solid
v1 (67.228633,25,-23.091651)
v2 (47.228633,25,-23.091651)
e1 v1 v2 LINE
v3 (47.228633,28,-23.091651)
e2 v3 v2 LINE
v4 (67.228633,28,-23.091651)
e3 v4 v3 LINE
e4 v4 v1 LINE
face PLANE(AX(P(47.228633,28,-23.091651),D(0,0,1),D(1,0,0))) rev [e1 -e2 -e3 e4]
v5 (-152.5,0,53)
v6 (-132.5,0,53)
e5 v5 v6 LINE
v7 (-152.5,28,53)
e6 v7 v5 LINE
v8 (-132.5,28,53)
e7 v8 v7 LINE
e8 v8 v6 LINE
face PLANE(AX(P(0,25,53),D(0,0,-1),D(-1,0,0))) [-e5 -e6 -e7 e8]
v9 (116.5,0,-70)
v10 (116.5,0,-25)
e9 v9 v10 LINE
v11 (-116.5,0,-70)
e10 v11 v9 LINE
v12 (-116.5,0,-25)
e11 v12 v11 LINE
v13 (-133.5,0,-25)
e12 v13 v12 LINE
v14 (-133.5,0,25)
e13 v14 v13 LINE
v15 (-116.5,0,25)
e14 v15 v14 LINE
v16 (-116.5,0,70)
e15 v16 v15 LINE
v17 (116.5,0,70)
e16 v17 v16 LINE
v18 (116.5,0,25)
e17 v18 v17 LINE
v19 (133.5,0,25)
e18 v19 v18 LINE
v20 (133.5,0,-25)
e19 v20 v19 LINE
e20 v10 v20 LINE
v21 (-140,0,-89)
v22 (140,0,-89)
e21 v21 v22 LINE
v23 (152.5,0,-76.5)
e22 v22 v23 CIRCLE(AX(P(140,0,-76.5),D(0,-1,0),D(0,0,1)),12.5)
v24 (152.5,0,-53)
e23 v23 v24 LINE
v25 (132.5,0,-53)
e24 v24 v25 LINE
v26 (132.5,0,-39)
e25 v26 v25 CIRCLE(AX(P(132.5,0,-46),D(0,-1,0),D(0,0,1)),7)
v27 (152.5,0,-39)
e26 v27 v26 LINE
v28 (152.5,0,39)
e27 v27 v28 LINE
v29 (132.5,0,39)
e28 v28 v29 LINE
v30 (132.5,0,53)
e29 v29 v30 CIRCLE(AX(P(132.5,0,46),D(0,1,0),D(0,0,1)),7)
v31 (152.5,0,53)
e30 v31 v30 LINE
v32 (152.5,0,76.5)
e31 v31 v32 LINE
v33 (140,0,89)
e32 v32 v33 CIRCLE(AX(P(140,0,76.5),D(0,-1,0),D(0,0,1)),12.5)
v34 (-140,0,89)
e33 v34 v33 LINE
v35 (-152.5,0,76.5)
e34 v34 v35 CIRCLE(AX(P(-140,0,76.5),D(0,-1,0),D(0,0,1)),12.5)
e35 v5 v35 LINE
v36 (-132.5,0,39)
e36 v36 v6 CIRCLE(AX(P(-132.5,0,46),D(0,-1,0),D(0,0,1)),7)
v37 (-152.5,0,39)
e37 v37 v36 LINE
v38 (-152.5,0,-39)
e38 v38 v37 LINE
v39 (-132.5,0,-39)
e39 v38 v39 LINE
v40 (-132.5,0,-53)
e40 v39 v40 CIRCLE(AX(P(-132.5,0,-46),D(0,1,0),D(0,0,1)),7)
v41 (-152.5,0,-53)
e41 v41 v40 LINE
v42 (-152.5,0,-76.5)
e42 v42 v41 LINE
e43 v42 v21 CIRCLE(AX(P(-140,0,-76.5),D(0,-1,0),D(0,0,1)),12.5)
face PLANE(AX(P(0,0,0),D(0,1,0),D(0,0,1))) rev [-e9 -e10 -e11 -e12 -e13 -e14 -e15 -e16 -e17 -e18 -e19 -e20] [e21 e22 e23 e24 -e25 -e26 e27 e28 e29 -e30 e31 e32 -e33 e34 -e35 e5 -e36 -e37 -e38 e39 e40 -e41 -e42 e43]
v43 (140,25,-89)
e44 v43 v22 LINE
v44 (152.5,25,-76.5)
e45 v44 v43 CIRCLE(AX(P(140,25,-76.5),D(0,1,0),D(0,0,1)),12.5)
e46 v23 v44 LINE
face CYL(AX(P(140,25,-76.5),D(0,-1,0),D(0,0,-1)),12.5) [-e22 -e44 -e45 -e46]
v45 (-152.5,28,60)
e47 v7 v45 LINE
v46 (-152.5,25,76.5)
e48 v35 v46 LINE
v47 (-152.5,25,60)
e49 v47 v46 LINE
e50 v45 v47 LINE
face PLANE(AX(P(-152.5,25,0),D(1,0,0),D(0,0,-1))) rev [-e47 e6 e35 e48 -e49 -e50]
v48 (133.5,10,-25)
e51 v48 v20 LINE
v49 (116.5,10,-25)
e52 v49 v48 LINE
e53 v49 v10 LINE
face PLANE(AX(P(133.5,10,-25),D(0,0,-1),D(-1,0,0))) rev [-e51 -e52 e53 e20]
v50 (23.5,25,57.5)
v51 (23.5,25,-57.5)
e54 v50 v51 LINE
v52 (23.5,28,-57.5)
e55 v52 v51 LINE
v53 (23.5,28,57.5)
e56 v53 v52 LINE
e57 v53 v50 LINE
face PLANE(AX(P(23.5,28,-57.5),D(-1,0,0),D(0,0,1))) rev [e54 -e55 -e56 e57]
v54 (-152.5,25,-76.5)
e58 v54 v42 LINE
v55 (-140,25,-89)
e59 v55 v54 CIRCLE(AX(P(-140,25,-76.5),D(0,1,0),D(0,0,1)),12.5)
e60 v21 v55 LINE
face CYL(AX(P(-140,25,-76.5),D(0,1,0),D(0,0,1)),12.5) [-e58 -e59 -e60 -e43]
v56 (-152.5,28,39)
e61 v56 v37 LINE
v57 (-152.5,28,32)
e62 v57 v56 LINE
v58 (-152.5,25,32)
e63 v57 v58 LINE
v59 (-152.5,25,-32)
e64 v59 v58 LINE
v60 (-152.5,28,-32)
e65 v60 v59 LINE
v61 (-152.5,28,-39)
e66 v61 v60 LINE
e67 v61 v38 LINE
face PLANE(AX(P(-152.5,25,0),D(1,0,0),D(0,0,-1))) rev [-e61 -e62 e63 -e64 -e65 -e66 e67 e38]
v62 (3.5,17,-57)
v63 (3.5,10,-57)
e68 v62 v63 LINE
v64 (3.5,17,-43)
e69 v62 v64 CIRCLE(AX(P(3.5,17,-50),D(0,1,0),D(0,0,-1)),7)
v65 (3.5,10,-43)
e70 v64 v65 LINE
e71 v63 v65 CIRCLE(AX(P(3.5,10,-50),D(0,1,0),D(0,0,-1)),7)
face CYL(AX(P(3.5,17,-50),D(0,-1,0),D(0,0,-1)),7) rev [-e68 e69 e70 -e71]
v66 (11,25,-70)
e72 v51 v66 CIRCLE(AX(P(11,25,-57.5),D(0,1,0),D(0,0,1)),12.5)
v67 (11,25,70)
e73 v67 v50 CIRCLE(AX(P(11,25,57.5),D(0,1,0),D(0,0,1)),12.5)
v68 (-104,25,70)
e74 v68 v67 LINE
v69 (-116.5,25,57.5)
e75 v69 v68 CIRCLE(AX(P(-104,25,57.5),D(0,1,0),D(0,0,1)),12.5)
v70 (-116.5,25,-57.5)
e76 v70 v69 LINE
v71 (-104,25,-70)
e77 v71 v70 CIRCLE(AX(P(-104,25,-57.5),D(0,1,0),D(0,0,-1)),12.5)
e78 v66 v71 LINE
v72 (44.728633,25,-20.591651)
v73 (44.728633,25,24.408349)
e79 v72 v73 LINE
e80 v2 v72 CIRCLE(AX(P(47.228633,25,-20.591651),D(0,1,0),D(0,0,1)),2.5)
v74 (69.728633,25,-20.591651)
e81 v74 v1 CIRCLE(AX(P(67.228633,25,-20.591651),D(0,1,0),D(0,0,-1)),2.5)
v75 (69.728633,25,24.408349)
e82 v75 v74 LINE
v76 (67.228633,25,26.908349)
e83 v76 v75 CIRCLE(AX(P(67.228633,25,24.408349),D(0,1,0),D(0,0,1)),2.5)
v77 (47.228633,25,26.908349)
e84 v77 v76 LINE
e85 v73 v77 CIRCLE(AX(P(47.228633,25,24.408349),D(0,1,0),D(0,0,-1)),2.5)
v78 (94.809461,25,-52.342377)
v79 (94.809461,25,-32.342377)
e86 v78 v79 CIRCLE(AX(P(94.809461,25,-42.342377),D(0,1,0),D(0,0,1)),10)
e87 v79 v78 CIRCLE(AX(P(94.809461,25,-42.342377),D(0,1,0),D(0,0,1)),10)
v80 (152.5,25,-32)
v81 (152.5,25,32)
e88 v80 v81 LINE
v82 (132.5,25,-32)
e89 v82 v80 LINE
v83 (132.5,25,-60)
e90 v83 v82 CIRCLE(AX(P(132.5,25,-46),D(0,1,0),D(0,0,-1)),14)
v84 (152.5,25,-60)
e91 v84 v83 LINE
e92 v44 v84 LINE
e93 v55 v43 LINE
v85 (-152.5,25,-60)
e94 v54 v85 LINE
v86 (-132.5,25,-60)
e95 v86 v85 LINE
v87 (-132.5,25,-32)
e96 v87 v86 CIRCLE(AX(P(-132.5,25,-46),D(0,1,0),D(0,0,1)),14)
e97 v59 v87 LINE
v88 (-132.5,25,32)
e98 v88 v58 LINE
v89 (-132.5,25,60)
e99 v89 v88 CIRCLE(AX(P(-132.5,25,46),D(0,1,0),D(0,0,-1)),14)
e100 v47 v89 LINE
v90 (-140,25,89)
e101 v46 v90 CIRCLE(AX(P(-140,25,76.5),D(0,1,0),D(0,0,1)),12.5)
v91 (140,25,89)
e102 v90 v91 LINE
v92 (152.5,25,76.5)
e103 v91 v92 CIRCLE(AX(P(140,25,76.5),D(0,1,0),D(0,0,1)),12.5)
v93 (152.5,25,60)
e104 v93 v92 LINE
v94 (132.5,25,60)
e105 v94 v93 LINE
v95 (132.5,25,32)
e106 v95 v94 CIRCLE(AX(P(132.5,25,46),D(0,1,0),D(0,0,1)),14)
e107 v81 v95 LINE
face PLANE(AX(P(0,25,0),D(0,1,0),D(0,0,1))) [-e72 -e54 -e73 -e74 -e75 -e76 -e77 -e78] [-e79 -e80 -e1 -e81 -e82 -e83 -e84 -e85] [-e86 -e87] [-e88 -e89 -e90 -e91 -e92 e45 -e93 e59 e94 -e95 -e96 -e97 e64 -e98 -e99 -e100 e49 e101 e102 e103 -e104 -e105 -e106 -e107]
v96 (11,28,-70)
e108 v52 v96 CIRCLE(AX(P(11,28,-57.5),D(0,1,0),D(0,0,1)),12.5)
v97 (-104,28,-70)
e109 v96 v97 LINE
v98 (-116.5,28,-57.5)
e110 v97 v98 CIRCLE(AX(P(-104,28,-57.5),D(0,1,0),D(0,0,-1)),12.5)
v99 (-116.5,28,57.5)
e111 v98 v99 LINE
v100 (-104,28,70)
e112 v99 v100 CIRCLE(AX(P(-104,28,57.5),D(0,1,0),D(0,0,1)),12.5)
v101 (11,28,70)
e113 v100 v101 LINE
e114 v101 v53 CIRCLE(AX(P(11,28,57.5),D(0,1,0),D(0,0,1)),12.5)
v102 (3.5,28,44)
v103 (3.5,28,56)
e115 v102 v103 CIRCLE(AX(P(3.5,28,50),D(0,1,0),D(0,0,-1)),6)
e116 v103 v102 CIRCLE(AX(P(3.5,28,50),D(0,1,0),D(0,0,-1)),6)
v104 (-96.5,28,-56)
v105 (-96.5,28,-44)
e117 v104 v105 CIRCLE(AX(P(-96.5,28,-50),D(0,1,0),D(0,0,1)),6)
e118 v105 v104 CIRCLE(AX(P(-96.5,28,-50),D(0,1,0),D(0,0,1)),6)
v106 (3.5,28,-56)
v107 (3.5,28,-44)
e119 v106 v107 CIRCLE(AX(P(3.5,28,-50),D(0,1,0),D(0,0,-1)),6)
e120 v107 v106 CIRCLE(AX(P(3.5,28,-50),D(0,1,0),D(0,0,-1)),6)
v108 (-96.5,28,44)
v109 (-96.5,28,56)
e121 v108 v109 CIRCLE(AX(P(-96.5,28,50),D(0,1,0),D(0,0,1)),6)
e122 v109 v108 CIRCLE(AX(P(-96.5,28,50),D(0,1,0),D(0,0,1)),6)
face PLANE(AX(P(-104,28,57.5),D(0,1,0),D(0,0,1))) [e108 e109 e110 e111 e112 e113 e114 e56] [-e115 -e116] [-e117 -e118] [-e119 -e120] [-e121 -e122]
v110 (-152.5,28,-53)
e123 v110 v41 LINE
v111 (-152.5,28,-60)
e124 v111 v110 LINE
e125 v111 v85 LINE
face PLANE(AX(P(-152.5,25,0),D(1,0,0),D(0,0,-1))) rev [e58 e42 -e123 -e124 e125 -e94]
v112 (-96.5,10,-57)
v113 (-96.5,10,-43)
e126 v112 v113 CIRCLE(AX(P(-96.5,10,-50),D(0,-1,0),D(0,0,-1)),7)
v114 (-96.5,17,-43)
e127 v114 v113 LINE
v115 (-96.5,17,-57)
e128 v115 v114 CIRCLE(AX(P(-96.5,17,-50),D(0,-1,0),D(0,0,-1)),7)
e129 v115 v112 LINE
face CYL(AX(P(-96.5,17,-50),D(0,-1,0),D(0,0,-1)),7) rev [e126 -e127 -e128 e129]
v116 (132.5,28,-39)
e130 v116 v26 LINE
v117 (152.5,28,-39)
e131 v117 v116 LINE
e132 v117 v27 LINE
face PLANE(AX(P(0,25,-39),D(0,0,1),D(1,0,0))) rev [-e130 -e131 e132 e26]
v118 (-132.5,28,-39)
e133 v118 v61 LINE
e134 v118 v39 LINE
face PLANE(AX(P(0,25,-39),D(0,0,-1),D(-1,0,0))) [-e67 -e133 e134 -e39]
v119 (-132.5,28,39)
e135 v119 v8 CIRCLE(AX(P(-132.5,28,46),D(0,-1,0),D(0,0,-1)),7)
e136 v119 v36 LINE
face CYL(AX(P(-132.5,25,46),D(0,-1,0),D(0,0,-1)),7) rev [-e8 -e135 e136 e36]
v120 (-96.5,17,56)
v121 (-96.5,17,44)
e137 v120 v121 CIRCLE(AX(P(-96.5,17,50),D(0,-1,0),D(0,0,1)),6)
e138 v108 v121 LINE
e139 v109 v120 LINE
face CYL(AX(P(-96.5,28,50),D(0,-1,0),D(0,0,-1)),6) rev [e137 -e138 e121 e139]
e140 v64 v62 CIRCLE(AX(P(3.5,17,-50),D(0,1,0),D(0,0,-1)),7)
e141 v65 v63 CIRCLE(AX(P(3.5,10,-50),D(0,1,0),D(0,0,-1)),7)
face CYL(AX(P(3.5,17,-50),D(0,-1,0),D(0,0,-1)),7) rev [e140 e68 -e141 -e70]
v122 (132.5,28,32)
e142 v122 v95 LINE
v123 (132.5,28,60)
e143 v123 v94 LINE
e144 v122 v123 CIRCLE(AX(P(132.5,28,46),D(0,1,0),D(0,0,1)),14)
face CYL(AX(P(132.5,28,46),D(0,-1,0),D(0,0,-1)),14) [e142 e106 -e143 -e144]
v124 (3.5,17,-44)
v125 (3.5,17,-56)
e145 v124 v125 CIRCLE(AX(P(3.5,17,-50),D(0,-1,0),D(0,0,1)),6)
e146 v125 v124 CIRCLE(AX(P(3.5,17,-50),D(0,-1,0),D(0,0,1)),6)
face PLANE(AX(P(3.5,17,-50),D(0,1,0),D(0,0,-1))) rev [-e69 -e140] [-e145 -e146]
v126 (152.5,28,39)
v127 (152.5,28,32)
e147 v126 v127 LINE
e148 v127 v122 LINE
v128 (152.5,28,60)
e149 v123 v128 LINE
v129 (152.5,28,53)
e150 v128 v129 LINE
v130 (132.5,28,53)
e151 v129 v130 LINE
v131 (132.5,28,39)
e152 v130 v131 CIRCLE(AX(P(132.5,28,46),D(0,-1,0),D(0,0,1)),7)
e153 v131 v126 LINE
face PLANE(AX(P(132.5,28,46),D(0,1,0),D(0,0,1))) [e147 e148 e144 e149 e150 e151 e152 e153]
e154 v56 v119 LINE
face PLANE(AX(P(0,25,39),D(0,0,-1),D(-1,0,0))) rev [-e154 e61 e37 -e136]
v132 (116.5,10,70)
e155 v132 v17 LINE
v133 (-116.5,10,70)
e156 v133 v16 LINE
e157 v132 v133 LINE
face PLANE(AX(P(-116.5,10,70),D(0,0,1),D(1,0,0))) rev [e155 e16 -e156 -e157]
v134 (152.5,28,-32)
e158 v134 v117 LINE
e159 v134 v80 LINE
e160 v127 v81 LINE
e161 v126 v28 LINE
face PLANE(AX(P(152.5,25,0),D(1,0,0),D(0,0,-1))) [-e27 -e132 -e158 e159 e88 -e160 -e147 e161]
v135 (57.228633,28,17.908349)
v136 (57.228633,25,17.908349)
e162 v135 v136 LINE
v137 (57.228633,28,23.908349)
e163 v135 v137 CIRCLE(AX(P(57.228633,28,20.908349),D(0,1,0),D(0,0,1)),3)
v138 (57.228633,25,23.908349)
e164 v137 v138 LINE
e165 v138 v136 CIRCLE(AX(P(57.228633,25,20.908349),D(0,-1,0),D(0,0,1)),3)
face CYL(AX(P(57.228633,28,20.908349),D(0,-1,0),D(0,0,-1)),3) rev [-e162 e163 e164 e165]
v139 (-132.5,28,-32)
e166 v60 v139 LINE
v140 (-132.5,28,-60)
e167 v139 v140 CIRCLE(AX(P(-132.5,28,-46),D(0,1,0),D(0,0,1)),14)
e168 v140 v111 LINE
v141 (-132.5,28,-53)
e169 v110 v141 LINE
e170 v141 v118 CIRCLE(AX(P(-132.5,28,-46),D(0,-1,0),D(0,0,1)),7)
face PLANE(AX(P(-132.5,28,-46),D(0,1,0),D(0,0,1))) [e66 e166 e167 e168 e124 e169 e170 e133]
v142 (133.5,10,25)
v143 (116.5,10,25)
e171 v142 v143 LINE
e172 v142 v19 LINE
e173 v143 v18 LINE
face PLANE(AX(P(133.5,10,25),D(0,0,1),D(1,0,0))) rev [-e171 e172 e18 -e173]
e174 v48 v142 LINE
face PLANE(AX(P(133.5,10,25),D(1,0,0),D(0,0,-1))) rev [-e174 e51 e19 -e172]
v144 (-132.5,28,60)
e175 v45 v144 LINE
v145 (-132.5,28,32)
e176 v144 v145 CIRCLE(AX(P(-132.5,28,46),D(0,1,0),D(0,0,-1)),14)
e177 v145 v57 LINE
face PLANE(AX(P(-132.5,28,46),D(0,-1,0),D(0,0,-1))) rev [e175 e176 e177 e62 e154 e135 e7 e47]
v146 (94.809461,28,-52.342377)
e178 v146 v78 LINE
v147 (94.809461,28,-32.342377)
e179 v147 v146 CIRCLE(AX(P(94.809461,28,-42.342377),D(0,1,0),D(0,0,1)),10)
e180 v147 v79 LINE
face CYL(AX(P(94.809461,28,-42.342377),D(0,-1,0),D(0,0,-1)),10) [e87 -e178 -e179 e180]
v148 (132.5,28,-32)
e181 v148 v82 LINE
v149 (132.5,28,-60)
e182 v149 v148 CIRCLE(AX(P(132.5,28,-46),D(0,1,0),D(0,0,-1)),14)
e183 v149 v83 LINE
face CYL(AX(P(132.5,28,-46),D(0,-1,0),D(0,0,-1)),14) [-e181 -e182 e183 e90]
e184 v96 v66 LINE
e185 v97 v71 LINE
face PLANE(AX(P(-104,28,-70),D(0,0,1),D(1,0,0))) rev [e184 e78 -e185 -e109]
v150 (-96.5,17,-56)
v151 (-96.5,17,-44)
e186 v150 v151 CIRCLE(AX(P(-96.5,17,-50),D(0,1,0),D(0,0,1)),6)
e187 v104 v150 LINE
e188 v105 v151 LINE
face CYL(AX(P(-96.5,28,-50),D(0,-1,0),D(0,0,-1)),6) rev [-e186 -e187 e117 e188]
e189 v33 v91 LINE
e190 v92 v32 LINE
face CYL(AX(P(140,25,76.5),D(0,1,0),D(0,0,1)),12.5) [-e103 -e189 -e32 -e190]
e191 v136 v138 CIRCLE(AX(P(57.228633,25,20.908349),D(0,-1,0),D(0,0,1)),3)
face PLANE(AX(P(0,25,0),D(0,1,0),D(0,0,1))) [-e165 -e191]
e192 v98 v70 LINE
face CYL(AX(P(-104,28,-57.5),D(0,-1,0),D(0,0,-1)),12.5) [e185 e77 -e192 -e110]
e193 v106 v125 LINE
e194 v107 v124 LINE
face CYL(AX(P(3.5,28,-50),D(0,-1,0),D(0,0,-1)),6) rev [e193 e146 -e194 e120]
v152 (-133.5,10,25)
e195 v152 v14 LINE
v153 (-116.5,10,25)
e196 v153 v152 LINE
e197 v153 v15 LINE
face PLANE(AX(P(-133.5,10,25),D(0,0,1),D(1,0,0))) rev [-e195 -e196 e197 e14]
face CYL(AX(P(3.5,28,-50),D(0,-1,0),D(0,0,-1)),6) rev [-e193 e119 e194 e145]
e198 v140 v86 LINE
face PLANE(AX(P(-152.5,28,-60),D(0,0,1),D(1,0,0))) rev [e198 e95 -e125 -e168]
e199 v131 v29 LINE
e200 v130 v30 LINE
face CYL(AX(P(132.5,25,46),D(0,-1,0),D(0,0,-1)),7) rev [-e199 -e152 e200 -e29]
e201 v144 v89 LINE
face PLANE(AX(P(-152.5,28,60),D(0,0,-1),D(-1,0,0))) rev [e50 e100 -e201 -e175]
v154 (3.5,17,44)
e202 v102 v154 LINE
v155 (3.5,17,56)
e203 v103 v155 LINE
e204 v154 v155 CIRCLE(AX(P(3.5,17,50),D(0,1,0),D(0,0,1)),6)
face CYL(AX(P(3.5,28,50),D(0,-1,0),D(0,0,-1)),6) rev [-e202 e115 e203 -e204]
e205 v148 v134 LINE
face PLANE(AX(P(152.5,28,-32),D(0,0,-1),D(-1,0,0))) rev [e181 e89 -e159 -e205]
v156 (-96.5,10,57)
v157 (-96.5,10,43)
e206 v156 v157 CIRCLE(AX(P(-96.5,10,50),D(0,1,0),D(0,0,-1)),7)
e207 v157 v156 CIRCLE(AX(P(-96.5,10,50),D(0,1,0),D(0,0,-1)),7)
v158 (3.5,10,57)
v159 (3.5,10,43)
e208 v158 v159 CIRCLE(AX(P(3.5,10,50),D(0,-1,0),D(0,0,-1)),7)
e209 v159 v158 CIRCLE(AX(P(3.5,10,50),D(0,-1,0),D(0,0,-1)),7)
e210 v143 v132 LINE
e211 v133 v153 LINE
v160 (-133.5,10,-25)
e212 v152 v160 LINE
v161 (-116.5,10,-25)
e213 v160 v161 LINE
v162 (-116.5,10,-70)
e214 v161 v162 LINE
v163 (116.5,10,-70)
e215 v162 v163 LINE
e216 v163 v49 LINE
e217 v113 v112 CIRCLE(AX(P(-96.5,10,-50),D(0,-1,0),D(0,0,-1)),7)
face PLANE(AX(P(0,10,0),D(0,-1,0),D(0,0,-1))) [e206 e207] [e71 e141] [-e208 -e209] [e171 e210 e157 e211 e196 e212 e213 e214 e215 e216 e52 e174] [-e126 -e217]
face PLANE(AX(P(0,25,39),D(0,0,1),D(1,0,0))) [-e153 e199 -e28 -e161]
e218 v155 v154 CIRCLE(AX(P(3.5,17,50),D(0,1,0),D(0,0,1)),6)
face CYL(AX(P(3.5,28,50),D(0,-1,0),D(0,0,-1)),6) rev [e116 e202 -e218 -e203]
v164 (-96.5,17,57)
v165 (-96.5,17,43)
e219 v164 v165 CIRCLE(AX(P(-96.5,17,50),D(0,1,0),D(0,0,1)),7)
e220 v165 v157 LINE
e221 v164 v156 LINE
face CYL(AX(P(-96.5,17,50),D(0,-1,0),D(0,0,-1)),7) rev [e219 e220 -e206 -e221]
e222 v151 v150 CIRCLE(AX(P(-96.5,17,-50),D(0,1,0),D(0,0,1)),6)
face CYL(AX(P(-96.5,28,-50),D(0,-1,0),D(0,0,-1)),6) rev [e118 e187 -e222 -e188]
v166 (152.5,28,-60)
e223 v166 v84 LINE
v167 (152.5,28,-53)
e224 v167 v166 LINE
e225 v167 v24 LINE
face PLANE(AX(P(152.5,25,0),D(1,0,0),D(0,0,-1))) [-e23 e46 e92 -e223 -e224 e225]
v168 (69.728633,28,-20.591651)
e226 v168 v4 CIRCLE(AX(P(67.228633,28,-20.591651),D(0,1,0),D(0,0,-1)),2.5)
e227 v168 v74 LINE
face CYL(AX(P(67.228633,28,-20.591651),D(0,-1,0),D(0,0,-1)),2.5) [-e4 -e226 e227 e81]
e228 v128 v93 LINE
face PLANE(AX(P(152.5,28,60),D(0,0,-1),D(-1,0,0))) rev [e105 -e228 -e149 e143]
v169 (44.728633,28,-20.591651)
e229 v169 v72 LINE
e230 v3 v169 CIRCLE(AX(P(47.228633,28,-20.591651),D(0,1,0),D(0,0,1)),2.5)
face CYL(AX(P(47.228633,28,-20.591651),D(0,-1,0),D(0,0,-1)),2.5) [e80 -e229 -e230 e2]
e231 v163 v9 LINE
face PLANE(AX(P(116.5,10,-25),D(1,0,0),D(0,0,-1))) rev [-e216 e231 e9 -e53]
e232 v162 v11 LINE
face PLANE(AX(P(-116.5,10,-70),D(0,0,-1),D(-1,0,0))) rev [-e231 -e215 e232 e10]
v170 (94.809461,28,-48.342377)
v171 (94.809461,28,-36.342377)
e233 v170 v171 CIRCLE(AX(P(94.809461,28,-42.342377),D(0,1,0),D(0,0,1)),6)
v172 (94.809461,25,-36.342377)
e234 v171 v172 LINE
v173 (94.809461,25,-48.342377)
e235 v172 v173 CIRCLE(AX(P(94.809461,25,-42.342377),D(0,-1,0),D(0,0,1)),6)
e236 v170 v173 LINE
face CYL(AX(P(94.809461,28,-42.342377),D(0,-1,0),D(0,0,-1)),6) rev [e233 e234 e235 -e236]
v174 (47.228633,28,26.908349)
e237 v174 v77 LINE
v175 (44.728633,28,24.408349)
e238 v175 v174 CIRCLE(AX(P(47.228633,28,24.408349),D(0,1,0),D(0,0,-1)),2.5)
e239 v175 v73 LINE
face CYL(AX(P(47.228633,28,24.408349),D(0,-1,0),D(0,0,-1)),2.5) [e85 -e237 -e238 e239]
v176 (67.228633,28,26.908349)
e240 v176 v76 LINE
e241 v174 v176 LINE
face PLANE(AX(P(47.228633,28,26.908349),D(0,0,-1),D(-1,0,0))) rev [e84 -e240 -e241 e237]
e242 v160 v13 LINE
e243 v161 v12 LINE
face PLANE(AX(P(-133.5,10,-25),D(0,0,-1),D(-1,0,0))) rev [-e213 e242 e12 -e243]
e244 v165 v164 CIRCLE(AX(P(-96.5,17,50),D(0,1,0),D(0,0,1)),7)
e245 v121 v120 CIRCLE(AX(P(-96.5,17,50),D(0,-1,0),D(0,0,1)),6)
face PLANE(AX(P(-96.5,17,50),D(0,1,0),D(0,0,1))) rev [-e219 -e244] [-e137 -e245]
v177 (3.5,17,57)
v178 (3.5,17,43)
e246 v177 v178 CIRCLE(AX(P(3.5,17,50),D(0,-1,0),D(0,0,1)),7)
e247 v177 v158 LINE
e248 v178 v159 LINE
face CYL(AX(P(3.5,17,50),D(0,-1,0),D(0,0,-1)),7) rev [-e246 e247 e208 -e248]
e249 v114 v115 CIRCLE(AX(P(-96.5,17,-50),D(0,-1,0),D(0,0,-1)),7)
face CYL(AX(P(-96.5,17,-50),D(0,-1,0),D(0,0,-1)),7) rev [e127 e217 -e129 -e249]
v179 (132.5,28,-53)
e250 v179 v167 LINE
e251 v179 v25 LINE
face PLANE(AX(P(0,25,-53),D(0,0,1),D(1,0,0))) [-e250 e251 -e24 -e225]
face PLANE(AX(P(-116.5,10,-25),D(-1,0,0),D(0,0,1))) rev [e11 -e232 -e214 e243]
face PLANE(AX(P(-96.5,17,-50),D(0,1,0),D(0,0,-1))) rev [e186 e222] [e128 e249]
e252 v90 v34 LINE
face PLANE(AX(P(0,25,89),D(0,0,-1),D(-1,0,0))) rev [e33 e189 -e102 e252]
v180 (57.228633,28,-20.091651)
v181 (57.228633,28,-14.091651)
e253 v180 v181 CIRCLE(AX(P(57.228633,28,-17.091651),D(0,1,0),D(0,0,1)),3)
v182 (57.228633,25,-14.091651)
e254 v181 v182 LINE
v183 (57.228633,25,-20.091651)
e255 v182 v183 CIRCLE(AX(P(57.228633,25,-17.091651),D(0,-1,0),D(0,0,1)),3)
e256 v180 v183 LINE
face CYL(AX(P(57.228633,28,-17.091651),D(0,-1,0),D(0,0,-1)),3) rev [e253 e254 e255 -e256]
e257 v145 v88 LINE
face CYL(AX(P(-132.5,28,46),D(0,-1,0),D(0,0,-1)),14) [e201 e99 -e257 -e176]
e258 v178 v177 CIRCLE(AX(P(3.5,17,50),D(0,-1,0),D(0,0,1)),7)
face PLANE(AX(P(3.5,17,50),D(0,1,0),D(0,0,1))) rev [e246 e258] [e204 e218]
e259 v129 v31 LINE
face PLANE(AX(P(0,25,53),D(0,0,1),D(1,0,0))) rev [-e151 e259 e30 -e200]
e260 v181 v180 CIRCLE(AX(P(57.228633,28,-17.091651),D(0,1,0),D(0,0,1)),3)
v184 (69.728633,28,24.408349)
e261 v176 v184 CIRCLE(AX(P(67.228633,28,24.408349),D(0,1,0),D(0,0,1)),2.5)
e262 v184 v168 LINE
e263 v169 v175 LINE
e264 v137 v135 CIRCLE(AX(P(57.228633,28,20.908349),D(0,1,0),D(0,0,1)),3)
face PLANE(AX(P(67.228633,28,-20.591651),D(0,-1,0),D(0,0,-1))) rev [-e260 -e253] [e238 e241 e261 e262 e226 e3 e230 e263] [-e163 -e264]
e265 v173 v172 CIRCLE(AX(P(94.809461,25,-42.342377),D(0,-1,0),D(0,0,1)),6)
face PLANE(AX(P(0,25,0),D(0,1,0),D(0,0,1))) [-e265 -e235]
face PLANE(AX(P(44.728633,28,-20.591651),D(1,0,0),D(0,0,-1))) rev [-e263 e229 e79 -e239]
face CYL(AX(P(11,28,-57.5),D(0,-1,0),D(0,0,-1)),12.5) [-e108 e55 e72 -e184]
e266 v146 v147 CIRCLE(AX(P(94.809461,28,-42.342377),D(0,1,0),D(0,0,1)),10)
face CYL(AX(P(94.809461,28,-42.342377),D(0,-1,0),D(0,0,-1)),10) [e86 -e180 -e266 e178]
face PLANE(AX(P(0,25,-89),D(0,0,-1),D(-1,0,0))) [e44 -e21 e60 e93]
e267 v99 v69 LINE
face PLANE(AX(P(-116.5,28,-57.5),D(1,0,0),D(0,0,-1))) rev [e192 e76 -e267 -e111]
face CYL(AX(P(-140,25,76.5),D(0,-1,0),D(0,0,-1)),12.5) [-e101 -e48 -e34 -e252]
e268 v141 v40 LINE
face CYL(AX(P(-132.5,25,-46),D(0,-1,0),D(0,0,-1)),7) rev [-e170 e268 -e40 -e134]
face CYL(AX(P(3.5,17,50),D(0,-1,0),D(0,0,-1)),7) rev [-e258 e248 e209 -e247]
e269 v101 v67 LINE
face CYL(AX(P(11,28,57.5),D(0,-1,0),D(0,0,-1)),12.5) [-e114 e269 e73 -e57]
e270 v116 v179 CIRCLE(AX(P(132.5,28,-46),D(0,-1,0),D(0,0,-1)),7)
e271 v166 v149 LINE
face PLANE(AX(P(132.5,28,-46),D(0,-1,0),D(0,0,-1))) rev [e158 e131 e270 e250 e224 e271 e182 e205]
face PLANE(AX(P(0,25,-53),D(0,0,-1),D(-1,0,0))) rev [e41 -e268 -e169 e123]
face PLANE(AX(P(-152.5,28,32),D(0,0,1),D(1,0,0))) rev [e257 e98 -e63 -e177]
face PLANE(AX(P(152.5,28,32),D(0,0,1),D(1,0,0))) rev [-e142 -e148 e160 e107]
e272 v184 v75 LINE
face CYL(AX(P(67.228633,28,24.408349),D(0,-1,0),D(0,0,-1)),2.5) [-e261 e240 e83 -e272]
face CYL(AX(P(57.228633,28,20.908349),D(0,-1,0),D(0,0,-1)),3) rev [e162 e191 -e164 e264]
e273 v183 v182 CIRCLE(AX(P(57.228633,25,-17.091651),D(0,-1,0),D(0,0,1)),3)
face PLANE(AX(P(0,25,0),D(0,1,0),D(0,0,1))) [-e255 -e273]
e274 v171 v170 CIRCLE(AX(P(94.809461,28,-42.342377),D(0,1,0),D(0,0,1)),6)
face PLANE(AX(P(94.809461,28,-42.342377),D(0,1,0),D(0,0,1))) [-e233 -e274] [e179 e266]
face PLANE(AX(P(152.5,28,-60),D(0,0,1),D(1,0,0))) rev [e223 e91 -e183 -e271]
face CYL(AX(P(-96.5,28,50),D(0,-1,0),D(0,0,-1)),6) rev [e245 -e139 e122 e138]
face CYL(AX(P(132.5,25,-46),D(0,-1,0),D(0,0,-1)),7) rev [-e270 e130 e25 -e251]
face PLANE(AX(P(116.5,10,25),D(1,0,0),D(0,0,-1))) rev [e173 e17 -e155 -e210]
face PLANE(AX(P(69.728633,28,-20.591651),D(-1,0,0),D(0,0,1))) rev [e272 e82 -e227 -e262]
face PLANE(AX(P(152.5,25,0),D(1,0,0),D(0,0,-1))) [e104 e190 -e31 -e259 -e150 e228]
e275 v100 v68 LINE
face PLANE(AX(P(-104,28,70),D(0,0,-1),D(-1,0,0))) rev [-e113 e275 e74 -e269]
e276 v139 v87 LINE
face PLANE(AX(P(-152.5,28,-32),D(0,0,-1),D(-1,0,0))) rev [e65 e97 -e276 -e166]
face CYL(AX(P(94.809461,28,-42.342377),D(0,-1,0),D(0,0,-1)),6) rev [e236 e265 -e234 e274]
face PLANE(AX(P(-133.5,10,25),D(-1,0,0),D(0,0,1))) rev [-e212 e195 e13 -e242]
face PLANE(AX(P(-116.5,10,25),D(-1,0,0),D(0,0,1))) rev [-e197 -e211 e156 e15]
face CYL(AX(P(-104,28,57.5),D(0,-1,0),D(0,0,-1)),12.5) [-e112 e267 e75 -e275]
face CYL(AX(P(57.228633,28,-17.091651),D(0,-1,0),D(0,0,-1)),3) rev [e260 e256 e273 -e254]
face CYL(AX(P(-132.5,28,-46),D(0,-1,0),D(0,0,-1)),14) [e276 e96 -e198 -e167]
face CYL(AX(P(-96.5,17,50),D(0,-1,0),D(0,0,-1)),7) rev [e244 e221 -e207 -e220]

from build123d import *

# Parameters (mm, degrees)
BASE_PLATE_305X178X25_DEPTH        = 25
ROUND_BOSS_3MM_DEPTH               = 3
RAISED_PADS_SKETCH_R               = 10
RAISED_PADS_SKETCH_R_2             = 6
RAISED_PADS_SKETCH_R_3             = 3
RAISED_PADS_3MM_DEPTH              = 3
CORNER_FILLETS_R12_5_R             = 12.5
SLOT_RECESSES_10_DEEP_DEPTH        = 10
PAD_START                          = -18
PAD_HOLE_A_POSITION_SKETCH_R       = 7
PAD_HOLE_A_DEPTH                   = 10
PAD_HOLE_B_REACH                   = 180.332
PAD_HOLE_B_POSITION_SKETCH_R       = 6
PAD_HOLES_MIRROR_2_COPY_1_SKETCH_R = 7
PAD_HOLES_MIRROR_2_COPY_1_DEPTH    = 10
PAD_HOLES_MIRROR_2_COPY_2_REACH    = 180.332
PAD_HOLES_MIRROR_2_COPY_2_SKETCH_R = 6


with BuildPart() as part:
    # Base Plate Profile Sketch → Base Plate 305x178x25 (new body)
    with BuildSketch(Plane(origin=(0, 0, 0), x_dir=(1, 0, 0), z_dir=(0, 1, 0))):
        with BuildLine():
            Line((152.5, 89), (-152.5, 89))
            Line((-152.5, 89), (-152.5, 53))
            Line((-152.5, 53), (-132.5, 53))
            ThreePointArc((-132.5, 53), (-125.5, 46), (-132.5, 39))
            Line((-132.5, 39), (-152.5, 39))
            Line((-152.5, 39), (-152.5, -39))
            Line((-152.5, -39), (-132.5, -39))
            ThreePointArc((-132.5, -39), (-125.5, -46), (-132.5, -53))
            Line((-132.5, -53), (-152.5, -53))
            Line((-152.5, -53), (-152.5, -89))
            Line((-152.5, -89), (152.5, -89))
            Line((152.5, -89), (152.5, -53))
            Line((152.5, -53), (132.5, -53))
            ThreePointArc((132.5, -53), (125.5, -46), (132.5, -39))
            Line((132.5, -39), (152.5, -39))
            Line((152.5, -39), (152.5, 39))
            Line((152.5, 39), (132.5, 39))
            ThreePointArc((132.5, 39), (125.5, 46), (132.5, 53))
            Line((132.5, 53), (152.5, 53))
            Line((152.5, 53), (152.5, 89))
        make_face()
    extrude(amount=BASE_PLATE_305X178X25_DEPTH)

    # Round Boss Sketch → Round Boss 3mm (add)
    with BuildSketch(Plane(origin=(0, 25, 0), x_dir=(1, 0, 0), z_dir=(0, 1, 0))):
        with BuildLine():
            Line((-152.5, 60), (-152.5, 53))
            Line((-152.5, 53), (-132.5, 53))
            ThreePointArc((-132.5, 53), (-125.5, 46), (-132.5, 39))
            Line((-132.5, 39), (-152.5, 39))
            Line((-152.5, 39), (-152.5, 32))
            Line((-152.5, 32), (-132.5, 32))
            ThreePointArc((-132.5, 32), (-118.5, 46), (-132.5, 60))
            Line((-132.5, 60), (-152.5, 60))
        make_face()
        with BuildLine():
            Line((152.5, 53), (132.5, 53))
            ThreePointArc((132.5, 53), (125.5, 46), (132.5, 39))
            Line((132.5, 39), (152.5, 39))
            Line((152.5, 39), (152.5, 32))
            Line((152.5, 32), (132.5, 32))
            ThreePointArc((132.5, 32), (118.5, 46), (132.5, 60))
            Line((132.5, 60), (152.5, 60))
            Line((152.5, 60), (152.5, 53))
        make_face()
        with BuildLine():
            Line((152.5, -39), (132.5, -39))
            ThreePointArc((132.5, -39), (125.5, -46), (132.5, -53))
            Line((132.5, -53), (152.5, -53))
            Line((152.5, -53), (152.5, -60))
            Line((152.5, -60), (132.5, -60))
            ThreePointArc((132.5, -60), (118.5, -46), (132.5, -32))
            Line((132.5, -32), (152.5, -32))
            Line((152.5, -32), (152.5, -39))
        make_face()
        with BuildLine():
            Line((-152.5, -53), (-132.5, -53))
            ThreePointArc((-132.5, -53), (-125.5, -46), (-132.5, -39))
            Line((-132.5, -39), (-152.5, -39))
            Line((-152.5, -39), (-152.5, -32))
            Line((-152.5, -32), (-132.5, -32))
            ThreePointArc((-132.5, -32), (-118.5, -46), (-132.5, -60))
            Line((-132.5, -60), (-152.5, -60))
            Line((-152.5, -60), (-152.5, -53))
        make_face()
    extrude(amount=ROUND_BOSS_3MM_DEPTH)

    # Raised Pads Sketch → Raised Pads 3mm (add)
    # profile 1 of 3: a face of its own
    with BuildSketch(Plane(origin=(0, 25, 0), x_dir=(1, 0, 0), z_dir=(0, 1, 0))):
        with Locations(Location((94.809461238, 42.342376818, 0), (0, 0, 270))):
            Circle(RAISED_PADS_SKETCH_R)
        with Locations(Location((94.809461238, 42.342376818, 0), (0, 0, 270))):
            Circle(RAISED_PADS_SKETCH_R_2, mode=Mode.SUBTRACT)
    # profile 2 of 3: a face of its own
    with BuildSketch(Plane(origin=(0, 25, 0), x_dir=(1, 0, 0), z_dir=(0, 1, 0))):
        with BuildLine():
            Line((-104, 70), (11, 70))
            ThreePointArc((11, 70), (19.838834765, 66.338834765), (23.5, 57.5))
            Line((23.5, 57.5), (23.5, -57.5))
            ThreePointArc((23.5, -57.5), (19.838834765, -66.338834765), (11, -70))
            Line((11, -70), (-104, -70))
            ThreePointArc((-104, -70), (-112.838834765, -66.338834765), (-116.5, -57.5))
            Line((-116.5, -57.5), (-116.5, 57.5))
            ThreePointArc((-116.5, 57.5), (-112.838834765, 66.338834765), (-104, 70))
        make_face()
        with Locations(Location((-96.5, 50, 0), (0, 0, 270))):
            Circle(RAISED_PADS_SKETCH_R_2, mode=Mode.SUBTRACT)
        with Locations(Location((-96.5, -50, 0), (0, 0, 270))):
            Circle(RAISED_PADS_SKETCH_R_2, mode=Mode.SUBTRACT)
        with Locations(Location((3.5, -50, 0), (0, 0, 90))):
            Circle(RAISED_PADS_SKETCH_R_2, mode=Mode.SUBTRACT)
        with Locations(Location((3.5, 50, 0), (0, 0, 90))):
            Circle(RAISED_PADS_SKETCH_R_2, mode=Mode.SUBTRACT)
    # profile 3 of 3: a face of its own
    with BuildSketch(Plane(origin=(0, 25, 0), x_dir=(1, 0, 0), z_dir=(0, 1, 0))):
        with BuildLine():
            Line((47.228633365, 23.091650714), (67.228633365, 23.091650714))
            ThreePointArc((67.228633365, 23.091650714), (68.996400318, 22.359417667), (69.728633365, 20.591650714))
            Line((69.728633365, 20.591650714), (69.728633365, -24.408349286))
            ThreePointArc((69.728633365, -24.408349286), (68.996400318, -26.176116239), (67.228633365, -26.908349286))
            Line((67.228633365, -26.908349286), (47.228633365, -26.908349286))
            ThreePointArc((47.228633365, -26.908349286), (45.460866412, -26.176116239), (44.728633365, -24.408349286))
            Line((44.728633365, -24.408349286), (44.728633365, 20.591650714))
            ThreePointArc((44.728633365, 20.591650714), (45.460866412, 22.359417667), (47.228633365, 23.091650714))
        make_face()
        with Locations(Location((57.228633365, 17.091650714, 0), (0, 0, 270))):
            Circle(RAISED_PADS_SKETCH_R_3, mode=Mode.SUBTRACT)
        with Locations(Location((57.228633365, -20.908349286, 0), (0, 0, 270))):
            Circle(RAISED_PADS_SKETCH_R_3, mode=Mode.SUBTRACT)
    extrude(amount=RAISED_PADS_3MM_DEPTH)

    # Corner Fillets R12.5
    corner_fillets_r12_5_edges = [part.edges().sort_by_distance(p)[0] for p in [
        (-152.5, 12.5, -89),
        (152.5, 12.5, -89),
        (152.5, 12.5, 89),
        (-152.5, 12.5, 89),
    ]]
    fillet(corner_fillets_r12_5_edges, radius=CORNER_FILLETS_R12_5_R)

    # Slot Recess Sketch → Slot Recesses 10 Deep (cut)
    with BuildSketch(Plane.XZ):
        Polygon((-133.5, 25), (-133.5, -25), (-116.5, -25), (-116.5, -70), (116.5, -70), (116.5, -25), (133.5, -25), (133.5, 25), (116.5, 25), (116.5, 70), (-116.5, 70), (-116.5, 25), align=None)
    extrude(amount=-SLOT_RECESSES_10_DEEP_DEPTH, mode=Mode.SUBTRACT)

    # Pad Hole A Position Sketch → Pad Hole A (cut)
    with BuildSketch(Plane(origin=(0, 25, 0), x_dir=(1, 0, 0), z_dir=(0, 1, 0)).offset(PAD_START)):
        with Locations(Location((-96.5, -50, 0), (0, 0, 90))):
            Circle(PAD_HOLE_A_POSITION_SKETCH_R)
    pad_hole_a = extrude(amount=PAD_HOLE_A_DEPTH, mode=Mode.SUBTRACT)

    # Pad Hole B Position Sketch → Pad Hole B (cut, up to next)
    with BuildSketch(Plane(origin=(0, 25, 0), x_dir=(1, 0, 0), z_dir=(0, 1, 0)), mode=Mode.PRIVATE) as pad_hole_b_sk1:
        with Locations(Location((-96.5, -50, 0), (0, 0, 270))):
            Circle(PAD_HOLE_B_POSITION_SKETCH_R)
    pad_hole_b_tool1 = extrude(pad_hole_b_sk1.sketch, amount=-PAD_HOLE_B_REACH, mode=Mode.PRIVATE) & part.part
    pad_hole_b = pad_hole_b_tool1.solids().sort_by_distance((-96.5, 25, 50))[0]
    add(pad_hole_b, mode=Mode.SUBTRACT)

    # Pad Holes Mirror 1: Pad Hole A, Pad Hole B across plane
    add(pad_hole_a.mirror(Plane.ZY.offset(46.5)), mode=Mode.SUBTRACT)
    add(pad_hole_b.mirror(Plane.ZY.offset(46.5)), mode=Mode.SUBTRACT)

    # Pad Holes Mirror 2: Pad Hole A, Pad Hole B across plane
    add(pad_hole_a.mirror(Plane.XY), mode=Mode.SUBTRACT)
    add(pad_hole_b.mirror(Plane.XY), mode=Mode.SUBTRACT)

    # Pad Holes Mirror 2 copy 1 sketch → Pad Holes Mirror 2 copy 1 (cut)
    with BuildSketch(Plane(origin=(-93, 25, 0), x_dir=(-1, 0, 0), z_dir=(0, 1, 0)).offset(PAD_START)):
        with Locations(Location((-96.5, -50, 0), (0, 0, 90))):
            Circle(PAD_HOLES_MIRROR_2_COPY_1_SKETCH_R)
    extrude(amount=PAD_HOLES_MIRROR_2_COPY_1_DEPTH, mode=Mode.SUBTRACT)

    # Pad Holes Mirror 2 copy 2 sketch → Pad Holes Mirror 2 copy 2 (cut, up to next)
    with BuildSketch(Plane(origin=(-93, 25, 0), x_dir=(-1, 0, 0), z_dir=(0, 1, 0)), mode=Mode.PRIVATE) as pad_holes_mirror_2_copy_2_sk1:
        with Locations(Location((-96.5, -50, 0), (0, 0, 270))):
            Circle(PAD_HOLES_MIRROR_2_COPY_2_SKETCH_R)
    pad_holes_mirror_2_copy_2_tool1 = extrude(pad_holes_mirror_2_copy_2_sk1.sketch, amount=-PAD_HOLES_MIRROR_2_COPY_2_REACH, mode=Mode.PRIVATE) & part.part
    add(pad_holes_mirror_2_copy_2_tool1.solids().sort_by_distance((3.5, 25, -50))[0], mode=Mode.SUBTRACT)


solid = part.part
